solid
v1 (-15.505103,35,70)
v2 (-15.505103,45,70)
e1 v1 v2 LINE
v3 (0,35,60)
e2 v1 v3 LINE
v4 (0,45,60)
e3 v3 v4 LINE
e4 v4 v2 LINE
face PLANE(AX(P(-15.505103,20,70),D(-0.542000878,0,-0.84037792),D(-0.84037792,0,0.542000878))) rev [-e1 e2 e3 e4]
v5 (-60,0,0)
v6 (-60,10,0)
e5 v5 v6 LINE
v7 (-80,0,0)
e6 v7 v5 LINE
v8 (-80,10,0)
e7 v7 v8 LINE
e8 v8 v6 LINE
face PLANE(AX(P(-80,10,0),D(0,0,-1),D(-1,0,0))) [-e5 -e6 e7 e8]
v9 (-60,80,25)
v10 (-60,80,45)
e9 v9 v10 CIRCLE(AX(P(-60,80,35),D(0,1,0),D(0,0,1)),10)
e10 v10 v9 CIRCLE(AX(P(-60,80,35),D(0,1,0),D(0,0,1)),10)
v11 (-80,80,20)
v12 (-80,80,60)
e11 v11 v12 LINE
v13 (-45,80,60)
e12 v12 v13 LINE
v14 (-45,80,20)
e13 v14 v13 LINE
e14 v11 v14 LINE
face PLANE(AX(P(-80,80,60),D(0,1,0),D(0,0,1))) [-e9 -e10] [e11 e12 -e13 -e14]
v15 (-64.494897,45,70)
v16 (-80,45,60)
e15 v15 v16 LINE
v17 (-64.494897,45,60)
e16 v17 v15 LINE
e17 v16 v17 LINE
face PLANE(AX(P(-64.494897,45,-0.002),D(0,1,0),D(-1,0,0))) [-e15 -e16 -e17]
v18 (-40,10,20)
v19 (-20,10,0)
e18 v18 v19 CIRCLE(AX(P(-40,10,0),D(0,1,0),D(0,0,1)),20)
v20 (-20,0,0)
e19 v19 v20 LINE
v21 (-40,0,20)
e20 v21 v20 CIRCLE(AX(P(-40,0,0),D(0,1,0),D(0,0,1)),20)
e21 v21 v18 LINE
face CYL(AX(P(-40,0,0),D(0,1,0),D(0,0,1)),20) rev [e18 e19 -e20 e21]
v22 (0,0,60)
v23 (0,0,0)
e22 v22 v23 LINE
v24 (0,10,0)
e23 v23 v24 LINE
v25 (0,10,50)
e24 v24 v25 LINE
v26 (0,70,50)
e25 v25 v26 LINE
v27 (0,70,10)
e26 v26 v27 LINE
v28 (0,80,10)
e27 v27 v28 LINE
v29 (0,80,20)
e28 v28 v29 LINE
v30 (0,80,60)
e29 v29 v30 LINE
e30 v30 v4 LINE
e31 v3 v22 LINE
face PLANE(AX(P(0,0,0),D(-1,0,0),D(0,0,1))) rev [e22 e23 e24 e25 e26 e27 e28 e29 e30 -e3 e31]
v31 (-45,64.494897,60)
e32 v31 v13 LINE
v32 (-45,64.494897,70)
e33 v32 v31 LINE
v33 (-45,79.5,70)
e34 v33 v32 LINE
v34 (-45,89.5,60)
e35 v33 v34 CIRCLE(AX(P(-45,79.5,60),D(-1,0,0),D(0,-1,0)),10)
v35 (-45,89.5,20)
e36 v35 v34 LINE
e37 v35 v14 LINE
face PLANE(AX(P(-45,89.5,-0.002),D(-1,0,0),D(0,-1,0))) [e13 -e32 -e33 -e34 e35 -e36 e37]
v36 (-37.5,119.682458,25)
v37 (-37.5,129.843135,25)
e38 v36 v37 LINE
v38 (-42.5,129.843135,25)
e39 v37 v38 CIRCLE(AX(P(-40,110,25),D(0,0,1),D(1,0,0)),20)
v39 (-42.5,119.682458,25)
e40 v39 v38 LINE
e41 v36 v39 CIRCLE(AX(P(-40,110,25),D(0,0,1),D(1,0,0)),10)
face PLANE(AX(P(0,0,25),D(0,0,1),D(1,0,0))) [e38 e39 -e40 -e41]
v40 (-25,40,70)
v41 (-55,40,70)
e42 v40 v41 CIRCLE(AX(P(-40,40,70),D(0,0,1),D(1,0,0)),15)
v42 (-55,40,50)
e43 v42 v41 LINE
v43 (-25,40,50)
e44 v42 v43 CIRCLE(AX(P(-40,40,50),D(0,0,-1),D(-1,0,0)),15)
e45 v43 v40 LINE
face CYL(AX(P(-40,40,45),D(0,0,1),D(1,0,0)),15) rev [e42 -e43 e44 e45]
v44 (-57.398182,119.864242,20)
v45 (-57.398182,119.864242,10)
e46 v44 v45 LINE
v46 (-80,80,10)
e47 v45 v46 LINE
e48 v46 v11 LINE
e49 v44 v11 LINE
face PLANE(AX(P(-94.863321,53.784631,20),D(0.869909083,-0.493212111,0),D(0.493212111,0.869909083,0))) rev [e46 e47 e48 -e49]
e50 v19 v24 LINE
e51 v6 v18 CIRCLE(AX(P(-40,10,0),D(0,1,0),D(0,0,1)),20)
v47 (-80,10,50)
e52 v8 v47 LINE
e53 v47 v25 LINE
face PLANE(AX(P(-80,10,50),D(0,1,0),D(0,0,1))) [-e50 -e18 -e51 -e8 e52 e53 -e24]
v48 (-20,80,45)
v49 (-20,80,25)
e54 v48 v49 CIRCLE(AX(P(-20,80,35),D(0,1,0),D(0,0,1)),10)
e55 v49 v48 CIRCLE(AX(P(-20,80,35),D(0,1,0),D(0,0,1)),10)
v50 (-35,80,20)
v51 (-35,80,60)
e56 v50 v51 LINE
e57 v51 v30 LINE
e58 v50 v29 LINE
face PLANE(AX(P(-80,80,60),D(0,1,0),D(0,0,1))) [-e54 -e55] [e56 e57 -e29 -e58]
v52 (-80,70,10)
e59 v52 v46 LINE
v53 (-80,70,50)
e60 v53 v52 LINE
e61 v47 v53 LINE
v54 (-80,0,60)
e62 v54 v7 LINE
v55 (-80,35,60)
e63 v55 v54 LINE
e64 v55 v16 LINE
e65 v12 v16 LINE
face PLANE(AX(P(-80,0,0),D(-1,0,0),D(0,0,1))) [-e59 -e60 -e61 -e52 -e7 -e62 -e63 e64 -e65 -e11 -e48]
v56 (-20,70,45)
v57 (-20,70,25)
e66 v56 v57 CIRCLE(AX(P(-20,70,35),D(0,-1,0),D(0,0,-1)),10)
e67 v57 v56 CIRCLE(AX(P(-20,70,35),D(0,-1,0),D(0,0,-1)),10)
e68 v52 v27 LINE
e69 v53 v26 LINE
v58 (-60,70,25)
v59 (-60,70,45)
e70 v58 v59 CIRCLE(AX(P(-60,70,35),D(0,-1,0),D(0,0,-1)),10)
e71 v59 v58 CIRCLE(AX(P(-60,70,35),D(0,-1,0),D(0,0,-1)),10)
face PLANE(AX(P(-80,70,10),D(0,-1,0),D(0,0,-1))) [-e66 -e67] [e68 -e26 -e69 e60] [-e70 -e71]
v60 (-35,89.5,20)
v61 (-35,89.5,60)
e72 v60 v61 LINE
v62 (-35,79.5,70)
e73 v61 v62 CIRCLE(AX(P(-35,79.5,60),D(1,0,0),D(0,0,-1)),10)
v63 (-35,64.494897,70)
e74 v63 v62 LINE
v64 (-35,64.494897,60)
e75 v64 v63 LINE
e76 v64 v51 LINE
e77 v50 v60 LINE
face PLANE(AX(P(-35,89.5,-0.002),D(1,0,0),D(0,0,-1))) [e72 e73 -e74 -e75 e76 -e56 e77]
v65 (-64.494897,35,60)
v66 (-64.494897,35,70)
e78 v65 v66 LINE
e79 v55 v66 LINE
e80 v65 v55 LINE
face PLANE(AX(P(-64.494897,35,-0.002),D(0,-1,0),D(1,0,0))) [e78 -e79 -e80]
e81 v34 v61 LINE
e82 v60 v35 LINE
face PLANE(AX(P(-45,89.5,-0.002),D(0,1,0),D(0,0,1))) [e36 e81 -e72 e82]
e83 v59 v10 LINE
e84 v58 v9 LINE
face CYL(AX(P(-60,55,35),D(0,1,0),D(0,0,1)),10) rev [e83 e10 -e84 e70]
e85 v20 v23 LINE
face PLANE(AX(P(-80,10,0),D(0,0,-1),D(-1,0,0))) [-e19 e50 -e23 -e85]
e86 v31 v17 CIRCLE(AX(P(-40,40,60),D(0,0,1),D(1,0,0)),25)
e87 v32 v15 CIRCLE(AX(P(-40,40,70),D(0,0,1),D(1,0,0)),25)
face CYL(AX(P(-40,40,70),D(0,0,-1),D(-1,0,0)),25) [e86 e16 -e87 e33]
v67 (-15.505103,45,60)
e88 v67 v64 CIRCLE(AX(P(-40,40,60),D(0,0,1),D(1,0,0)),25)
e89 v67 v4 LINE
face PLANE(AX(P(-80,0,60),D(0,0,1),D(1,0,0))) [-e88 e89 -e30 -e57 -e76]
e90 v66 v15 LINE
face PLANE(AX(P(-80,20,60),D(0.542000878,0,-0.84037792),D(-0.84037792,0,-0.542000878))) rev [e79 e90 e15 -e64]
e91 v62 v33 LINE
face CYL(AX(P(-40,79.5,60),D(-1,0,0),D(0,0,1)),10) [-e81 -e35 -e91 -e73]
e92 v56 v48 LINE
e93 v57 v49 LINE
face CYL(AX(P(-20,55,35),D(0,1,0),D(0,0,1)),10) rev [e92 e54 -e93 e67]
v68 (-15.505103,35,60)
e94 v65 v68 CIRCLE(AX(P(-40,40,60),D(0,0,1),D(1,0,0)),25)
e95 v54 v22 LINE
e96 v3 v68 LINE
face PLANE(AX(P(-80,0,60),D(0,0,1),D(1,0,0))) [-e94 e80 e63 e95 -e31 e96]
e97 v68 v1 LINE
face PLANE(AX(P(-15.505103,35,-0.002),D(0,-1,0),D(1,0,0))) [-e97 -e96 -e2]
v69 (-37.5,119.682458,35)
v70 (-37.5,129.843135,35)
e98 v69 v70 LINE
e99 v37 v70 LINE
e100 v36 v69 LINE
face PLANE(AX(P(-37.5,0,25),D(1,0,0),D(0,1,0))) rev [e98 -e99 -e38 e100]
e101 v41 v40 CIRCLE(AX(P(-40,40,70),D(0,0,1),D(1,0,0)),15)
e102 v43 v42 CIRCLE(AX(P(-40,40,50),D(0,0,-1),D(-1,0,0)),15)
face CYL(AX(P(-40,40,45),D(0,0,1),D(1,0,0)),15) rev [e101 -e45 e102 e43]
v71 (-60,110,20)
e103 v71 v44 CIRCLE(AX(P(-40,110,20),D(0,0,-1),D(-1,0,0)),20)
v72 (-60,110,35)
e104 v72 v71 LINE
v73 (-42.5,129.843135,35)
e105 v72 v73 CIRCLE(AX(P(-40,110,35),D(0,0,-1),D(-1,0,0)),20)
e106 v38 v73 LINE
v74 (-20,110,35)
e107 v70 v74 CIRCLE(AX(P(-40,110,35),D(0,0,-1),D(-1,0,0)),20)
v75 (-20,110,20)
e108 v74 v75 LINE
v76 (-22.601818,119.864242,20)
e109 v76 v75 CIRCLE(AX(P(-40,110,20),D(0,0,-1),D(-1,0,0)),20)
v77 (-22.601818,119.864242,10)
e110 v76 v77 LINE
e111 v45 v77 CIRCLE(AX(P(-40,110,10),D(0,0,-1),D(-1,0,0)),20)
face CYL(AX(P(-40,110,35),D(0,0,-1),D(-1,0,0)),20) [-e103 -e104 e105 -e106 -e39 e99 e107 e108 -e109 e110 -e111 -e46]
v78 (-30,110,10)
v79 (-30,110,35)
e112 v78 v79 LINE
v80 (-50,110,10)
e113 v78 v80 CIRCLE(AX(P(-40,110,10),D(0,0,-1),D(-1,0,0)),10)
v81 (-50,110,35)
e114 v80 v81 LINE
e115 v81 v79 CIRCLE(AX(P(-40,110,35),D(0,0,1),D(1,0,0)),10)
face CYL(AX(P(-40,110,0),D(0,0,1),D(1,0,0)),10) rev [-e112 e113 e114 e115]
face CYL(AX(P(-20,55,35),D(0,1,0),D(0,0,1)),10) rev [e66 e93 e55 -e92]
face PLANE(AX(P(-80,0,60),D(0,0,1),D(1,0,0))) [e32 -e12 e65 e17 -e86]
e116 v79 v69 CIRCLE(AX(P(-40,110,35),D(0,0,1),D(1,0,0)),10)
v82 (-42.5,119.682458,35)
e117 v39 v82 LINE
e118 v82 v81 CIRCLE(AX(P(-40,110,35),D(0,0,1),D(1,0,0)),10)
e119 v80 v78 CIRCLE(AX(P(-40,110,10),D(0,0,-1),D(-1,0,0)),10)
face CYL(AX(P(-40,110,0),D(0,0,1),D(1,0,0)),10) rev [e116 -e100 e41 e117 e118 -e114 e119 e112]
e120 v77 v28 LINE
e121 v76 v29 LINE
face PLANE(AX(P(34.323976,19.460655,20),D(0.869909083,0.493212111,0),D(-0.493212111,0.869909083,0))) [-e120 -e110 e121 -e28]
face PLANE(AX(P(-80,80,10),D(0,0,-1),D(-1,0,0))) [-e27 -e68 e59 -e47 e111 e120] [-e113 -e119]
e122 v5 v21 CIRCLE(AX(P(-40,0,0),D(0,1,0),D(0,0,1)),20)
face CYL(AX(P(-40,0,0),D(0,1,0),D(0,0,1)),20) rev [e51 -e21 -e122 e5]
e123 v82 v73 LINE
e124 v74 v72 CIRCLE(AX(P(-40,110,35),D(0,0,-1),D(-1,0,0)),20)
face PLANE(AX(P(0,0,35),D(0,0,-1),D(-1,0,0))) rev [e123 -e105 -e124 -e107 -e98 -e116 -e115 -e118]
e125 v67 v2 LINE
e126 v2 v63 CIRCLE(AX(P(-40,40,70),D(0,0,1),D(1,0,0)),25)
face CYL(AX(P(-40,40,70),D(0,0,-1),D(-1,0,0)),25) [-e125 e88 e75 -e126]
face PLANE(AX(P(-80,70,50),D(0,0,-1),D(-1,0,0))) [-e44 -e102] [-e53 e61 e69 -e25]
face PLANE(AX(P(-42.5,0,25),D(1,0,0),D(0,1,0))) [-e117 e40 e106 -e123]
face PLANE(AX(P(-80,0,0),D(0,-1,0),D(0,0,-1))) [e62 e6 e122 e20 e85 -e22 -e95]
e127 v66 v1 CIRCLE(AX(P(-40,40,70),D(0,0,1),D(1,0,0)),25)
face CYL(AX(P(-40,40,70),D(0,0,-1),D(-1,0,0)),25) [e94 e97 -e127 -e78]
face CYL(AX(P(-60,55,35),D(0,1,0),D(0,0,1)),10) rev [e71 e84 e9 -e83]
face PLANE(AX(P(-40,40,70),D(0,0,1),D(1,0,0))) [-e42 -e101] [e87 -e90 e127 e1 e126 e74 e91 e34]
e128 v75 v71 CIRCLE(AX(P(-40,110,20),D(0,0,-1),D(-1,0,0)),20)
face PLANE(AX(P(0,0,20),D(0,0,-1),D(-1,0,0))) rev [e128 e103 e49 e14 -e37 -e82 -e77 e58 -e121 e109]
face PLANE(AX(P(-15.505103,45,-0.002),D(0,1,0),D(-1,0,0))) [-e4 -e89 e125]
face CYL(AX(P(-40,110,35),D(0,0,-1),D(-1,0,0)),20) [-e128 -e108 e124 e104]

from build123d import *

# Parameters (mm, degrees)
C_FRAME_BODY_DEPTH        = 80
FRONT_BOSS_SKETCH_R       = 25
FRONT_BOSS_50_DEPTH       = 10
TOP_LUG_GUSSET_DEPTH      = 10
SKETCH3_3_R               = 20
TOP_LUG_RING_DEPTH        = 25
LOWER_RIB_REACH           = 169.929
LOWER_RIB_SKETCH_W        = 10
LOWER_RIB_SKETCH_H        = 9.5
RIB_EXTENSION_REACH       = 135.041
RIB_EXTENSION_SKETCH_W    = 10
RIB_EXTENSION_SKETCH_H    = 10
RIB_FILLET_R10_R          = 10
CONNECTING_STRAP_REACH    = 169.929
CONNECTING_STRAP_SKETCH_W = 15.505102572
CONNECTING_STRAP_SKETCH_H = 10
STRAP_RELIEF_CUT_DEPTH    = 25
FRONT_BORE_SKETCH_R       = 15
FRONT_BORE_30_DEPTH       = 25
TOP_HOLES_SKETCH_R        = 10
TOP_FACE_HOLES_DEPTH      = 25
LUG_BORE_DEPTH            = 157.604597634
LUG_CLAMP_SLOT_DEPTH      = 10
BASE_RELIEF_SKETCH_R      = 20
BASE_RELIEF_CUT_40_DEPTH  = 10


with BuildPart() as part:
    # C-Frame Profile Sketch → C-Frame Body (new body)
    with BuildSketch(Plane(origin=(0, 0, 0), x_dir=(0, 0, -1), z_dir=(1, 0, 0))):
        Polygon((0, 0), (-60, 0), (-60, 80), (-10, 80), (-10, 70), (-50, 70), (-50, 10), (0, 10), align=None)
    extrude(amount=-C_FRAME_BODY_DEPTH)

    # Front Boss Sketch → Front Boss _50 (add)
    with BuildSketch(Plane.XY.offset(60)):
        with Locations((-40, 40)):
            Circle(FRONT_BOSS_SKETCH_R)
    extrude(amount=FRONT_BOSS_50_DEPTH)

    # Top Lug Sketch → Top Lug Gusset (add)
    with BuildSketch(Plane(origin=(0, 0, 10), x_dir=(-1, 0, 0), z_dir=(0, 0, -1))):
        with BuildLine():
            ThreePointArc((60, 110), (34.899197777, 90.661390518), (22.601818332, 119.864242224))
            Line((22.601818332, 119.864242224), (0, 80))
            Line((0, 80), (80, 80))
            Line((80, 80), (57.398181668, 119.864242224))
            ThreePointArc((57.398181668, 119.864242224), (59.338609482, 115.100802223), (60, 110))
        make_face()
    extrude(amount=-TOP_LUG_GUSSET_DEPTH)

    # Sketch3_3 → Top Lug Ring (add)
    with BuildSketch(Plane(origin=(0, 0, 10), x_dir=(-1, 0, 0), z_dir=(0, 0, -1))):
        with Locations((40, 110)):
            Circle(SKETCH3_3_R)
    extrude(amount=-TOP_LUG_RING_DEPTH)

    # Lower Rib Sketch → Lower Rib (add, up to next)
    with BuildSketch(Plane.XY.offset(70), mode=Mode.PRIVATE) as lower_rib_sk1:
        with Locations((-40, 84.75)):
            Rectangle(LOWER_RIB_SKETCH_W, LOWER_RIB_SKETCH_H)
    lower_rib_tool1 = extrude(lower_rib_sk1.sketch, amount=-LOWER_RIB_REACH, mode=Mode.PRIVATE) - part.part
    add(lower_rib_tool1.solids().sort_by_distance((-40, 84.75, 70))[0])

    # Rib Extension Sketch → Rib Extension (add, up to next)
    with BuildSketch(Plane.XZ.offset(-80), mode=Mode.PRIVATE) as rib_extension_sk1:
        with Locations((-40, 65)):
            Rectangle(RIB_EXTENSION_SKETCH_W, RIB_EXTENSION_SKETCH_H)
    rib_extension_tool1 = extrude(rib_extension_sk1.sketch, amount=RIB_EXTENSION_REACH, mode=Mode.PRIVATE) - part.part
    add(rib_extension_tool1.solids().sort_by_distance((-40, 80, 65))[0])

    # Rib Fillet R10
    rib_fillet_r10_edges = [part.edges().sort_by_distance(p)[0] for p in [
        (-40, 89.5, 70),
    ]]
    fillet(rib_fillet_r10_edges, radius=RIB_FILLET_R10_R)

    # Connecting Strap Sketch → Connecting Strap (add, up to next)
    with BuildSketch(Plane.XY.offset(70), mode=Mode.PRIVATE) as connecting_strap_sk1:
        with Locations((-7.752551286, 40)):
            Rectangle(CONNECTING_STRAP_SKETCH_W, CONNECTING_STRAP_SKETCH_H)
    connecting_strap_tool1 = extrude(connecting_strap_sk1.sketch, amount=-CONNECTING_STRAP_REACH, mode=Mode.PRIVATE) - part.part
    # Connecting Strap Sketch → Connecting Strap (add, up to next)
    with BuildSketch(Plane.XY.offset(70), mode=Mode.PRIVATE) as connecting_strap_sk2:
        with Locations((-72.247448714, 40)):
            Rectangle(CONNECTING_STRAP_SKETCH_W, CONNECTING_STRAP_SKETCH_H)
    connecting_strap_tool2 = extrude(connecting_strap_sk2.sketch, amount=-CONNECTING_STRAP_REACH, mode=Mode.PRIVATE) - part.part
    add(connecting_strap_tool1.solids().sort_by_distance((-7.752551, 40, 70))[0])
    add(connecting_strap_tool2.solids().sort_by_distance((-72.247449, 40, 70))[0])

    # Strap Relief Sketch → Strap Relief Cut (cut)
    with BuildSketch(Plane(origin=(0, 45, 0), x_dir=(1, 0, 0), z_dir=(0, 1, 0))):
        Polygon((-15.505102572, -70), (0, -60), (0, -70), align=None)
        Polygon((-80, -60), (-64.494897428, -70), (-80, -70), align=None)
    extrude(amount=-STRAP_RELIEF_CUT_DEPTH, mode=Mode.SUBTRACT)

    # Front Bore Sketch → Front Bore _30 (cut)
    with BuildSketch(Plane.XY.offset(70)):
        with Locations((-40, 40)):
            Circle(FRONT_BORE_SKETCH_R)
    extrude(amount=-FRONT_BORE_30_DEPTH, mode=Mode.SUBTRACT)

    # Top Holes Sketch → Top Face Holes (cut)
    with BuildSketch(Plane(origin=(0, 80, 0), x_dir=(1, 0, 0), z_dir=(0, 1, 0))):
        with Locations(Location((-20, -35, 0), (0, 0, 270))):
            Circle(TOP_HOLES_SKETCH_R)
        with Locations(Location((-60, -35, 0), (0, 0, 270))):
            Circle(TOP_HOLES_SKETCH_R)
    extrude(amount=-TOP_FACE_HOLES_DEPTH, mode=Mode.SUBTRACT)

    # Lug Bore and Slot Sketch → Lug Bore (cut, through all)
    with BuildSketch(Plane.XY.offset(35)):
        with BuildLine():
            ThreePointArc((-37.5, 119.682458366), (-40, 120), (-42.5, 119.682458366))
            Line((-42.5, 119.682458366), (-37.5, 119.682458366))
        make_face()
        with BuildLine():
            Line((-37.5, 119.682458366), (-42.5, 119.682458366))
            ThreePointArc((-42.5, 119.682458366), (-46.123724357, 102.09430585), (-30, 110))
            ThreePointArc((-30, 110), (-32.09430585, 116.123724357), (-37.5, 119.682458366))
        make_face()
        with BuildLine():
            ThreePointArc((-37.5, 119.682458366), (-40, 120), (-42.5, 119.682458366))
            Line((-42.5, 119.682458366), (-37.5, 119.682458366))
        make_face()
        with BuildLine():
            Line((-37.5, 119.682458366), (-42.5, 119.682458366))
            ThreePointArc((-42.5, 119.682458366), (-46.123724357, 102.09430585), (-30, 110))
            ThreePointArc((-30, 110), (-32.09430585, 116.123724357), (-37.5, 119.682458366))
        make_face()
    extrude(amount=-LUG_BORE_DEPTH, mode=Mode.SUBTRACT)

    # Sketch14_3 → Lug Clamp Slot (cut)
    with BuildSketch(Plane.XY.offset(35)):
        with BuildLine():
            Line((-42.5, 129.843134833), (-42.5, 119.682458366))
            ThreePointArc((-42.5, 119.682458366), (-40, 120), (-37.5, 119.682458366))
            Line((-37.5, 119.682458366), (-37.5, 129.843134833))
            ThreePointArc((-37.5, 129.843134833), (-40, 130), (-42.5, 129.843134833))
        make_face()
    extrude(amount=-LUG_CLAMP_SLOT_DEPTH, mode=Mode.SUBTRACT)

    # Base Relief Sketch → Base Relief Cut _40 (cut)
    with BuildSketch(Plane(origin=(0, 10, 0), x_dir=(1, 0, 0), z_dir=(0, 1, 0))):
        with Locations((-40, 0)):
            Circle(BASE_RELIEF_SKETCH_R)
    extrude(amount=-BASE_RELIEF_CUT_40_DEPTH, mode=Mode.SUBTRACT)


solid = part.part
